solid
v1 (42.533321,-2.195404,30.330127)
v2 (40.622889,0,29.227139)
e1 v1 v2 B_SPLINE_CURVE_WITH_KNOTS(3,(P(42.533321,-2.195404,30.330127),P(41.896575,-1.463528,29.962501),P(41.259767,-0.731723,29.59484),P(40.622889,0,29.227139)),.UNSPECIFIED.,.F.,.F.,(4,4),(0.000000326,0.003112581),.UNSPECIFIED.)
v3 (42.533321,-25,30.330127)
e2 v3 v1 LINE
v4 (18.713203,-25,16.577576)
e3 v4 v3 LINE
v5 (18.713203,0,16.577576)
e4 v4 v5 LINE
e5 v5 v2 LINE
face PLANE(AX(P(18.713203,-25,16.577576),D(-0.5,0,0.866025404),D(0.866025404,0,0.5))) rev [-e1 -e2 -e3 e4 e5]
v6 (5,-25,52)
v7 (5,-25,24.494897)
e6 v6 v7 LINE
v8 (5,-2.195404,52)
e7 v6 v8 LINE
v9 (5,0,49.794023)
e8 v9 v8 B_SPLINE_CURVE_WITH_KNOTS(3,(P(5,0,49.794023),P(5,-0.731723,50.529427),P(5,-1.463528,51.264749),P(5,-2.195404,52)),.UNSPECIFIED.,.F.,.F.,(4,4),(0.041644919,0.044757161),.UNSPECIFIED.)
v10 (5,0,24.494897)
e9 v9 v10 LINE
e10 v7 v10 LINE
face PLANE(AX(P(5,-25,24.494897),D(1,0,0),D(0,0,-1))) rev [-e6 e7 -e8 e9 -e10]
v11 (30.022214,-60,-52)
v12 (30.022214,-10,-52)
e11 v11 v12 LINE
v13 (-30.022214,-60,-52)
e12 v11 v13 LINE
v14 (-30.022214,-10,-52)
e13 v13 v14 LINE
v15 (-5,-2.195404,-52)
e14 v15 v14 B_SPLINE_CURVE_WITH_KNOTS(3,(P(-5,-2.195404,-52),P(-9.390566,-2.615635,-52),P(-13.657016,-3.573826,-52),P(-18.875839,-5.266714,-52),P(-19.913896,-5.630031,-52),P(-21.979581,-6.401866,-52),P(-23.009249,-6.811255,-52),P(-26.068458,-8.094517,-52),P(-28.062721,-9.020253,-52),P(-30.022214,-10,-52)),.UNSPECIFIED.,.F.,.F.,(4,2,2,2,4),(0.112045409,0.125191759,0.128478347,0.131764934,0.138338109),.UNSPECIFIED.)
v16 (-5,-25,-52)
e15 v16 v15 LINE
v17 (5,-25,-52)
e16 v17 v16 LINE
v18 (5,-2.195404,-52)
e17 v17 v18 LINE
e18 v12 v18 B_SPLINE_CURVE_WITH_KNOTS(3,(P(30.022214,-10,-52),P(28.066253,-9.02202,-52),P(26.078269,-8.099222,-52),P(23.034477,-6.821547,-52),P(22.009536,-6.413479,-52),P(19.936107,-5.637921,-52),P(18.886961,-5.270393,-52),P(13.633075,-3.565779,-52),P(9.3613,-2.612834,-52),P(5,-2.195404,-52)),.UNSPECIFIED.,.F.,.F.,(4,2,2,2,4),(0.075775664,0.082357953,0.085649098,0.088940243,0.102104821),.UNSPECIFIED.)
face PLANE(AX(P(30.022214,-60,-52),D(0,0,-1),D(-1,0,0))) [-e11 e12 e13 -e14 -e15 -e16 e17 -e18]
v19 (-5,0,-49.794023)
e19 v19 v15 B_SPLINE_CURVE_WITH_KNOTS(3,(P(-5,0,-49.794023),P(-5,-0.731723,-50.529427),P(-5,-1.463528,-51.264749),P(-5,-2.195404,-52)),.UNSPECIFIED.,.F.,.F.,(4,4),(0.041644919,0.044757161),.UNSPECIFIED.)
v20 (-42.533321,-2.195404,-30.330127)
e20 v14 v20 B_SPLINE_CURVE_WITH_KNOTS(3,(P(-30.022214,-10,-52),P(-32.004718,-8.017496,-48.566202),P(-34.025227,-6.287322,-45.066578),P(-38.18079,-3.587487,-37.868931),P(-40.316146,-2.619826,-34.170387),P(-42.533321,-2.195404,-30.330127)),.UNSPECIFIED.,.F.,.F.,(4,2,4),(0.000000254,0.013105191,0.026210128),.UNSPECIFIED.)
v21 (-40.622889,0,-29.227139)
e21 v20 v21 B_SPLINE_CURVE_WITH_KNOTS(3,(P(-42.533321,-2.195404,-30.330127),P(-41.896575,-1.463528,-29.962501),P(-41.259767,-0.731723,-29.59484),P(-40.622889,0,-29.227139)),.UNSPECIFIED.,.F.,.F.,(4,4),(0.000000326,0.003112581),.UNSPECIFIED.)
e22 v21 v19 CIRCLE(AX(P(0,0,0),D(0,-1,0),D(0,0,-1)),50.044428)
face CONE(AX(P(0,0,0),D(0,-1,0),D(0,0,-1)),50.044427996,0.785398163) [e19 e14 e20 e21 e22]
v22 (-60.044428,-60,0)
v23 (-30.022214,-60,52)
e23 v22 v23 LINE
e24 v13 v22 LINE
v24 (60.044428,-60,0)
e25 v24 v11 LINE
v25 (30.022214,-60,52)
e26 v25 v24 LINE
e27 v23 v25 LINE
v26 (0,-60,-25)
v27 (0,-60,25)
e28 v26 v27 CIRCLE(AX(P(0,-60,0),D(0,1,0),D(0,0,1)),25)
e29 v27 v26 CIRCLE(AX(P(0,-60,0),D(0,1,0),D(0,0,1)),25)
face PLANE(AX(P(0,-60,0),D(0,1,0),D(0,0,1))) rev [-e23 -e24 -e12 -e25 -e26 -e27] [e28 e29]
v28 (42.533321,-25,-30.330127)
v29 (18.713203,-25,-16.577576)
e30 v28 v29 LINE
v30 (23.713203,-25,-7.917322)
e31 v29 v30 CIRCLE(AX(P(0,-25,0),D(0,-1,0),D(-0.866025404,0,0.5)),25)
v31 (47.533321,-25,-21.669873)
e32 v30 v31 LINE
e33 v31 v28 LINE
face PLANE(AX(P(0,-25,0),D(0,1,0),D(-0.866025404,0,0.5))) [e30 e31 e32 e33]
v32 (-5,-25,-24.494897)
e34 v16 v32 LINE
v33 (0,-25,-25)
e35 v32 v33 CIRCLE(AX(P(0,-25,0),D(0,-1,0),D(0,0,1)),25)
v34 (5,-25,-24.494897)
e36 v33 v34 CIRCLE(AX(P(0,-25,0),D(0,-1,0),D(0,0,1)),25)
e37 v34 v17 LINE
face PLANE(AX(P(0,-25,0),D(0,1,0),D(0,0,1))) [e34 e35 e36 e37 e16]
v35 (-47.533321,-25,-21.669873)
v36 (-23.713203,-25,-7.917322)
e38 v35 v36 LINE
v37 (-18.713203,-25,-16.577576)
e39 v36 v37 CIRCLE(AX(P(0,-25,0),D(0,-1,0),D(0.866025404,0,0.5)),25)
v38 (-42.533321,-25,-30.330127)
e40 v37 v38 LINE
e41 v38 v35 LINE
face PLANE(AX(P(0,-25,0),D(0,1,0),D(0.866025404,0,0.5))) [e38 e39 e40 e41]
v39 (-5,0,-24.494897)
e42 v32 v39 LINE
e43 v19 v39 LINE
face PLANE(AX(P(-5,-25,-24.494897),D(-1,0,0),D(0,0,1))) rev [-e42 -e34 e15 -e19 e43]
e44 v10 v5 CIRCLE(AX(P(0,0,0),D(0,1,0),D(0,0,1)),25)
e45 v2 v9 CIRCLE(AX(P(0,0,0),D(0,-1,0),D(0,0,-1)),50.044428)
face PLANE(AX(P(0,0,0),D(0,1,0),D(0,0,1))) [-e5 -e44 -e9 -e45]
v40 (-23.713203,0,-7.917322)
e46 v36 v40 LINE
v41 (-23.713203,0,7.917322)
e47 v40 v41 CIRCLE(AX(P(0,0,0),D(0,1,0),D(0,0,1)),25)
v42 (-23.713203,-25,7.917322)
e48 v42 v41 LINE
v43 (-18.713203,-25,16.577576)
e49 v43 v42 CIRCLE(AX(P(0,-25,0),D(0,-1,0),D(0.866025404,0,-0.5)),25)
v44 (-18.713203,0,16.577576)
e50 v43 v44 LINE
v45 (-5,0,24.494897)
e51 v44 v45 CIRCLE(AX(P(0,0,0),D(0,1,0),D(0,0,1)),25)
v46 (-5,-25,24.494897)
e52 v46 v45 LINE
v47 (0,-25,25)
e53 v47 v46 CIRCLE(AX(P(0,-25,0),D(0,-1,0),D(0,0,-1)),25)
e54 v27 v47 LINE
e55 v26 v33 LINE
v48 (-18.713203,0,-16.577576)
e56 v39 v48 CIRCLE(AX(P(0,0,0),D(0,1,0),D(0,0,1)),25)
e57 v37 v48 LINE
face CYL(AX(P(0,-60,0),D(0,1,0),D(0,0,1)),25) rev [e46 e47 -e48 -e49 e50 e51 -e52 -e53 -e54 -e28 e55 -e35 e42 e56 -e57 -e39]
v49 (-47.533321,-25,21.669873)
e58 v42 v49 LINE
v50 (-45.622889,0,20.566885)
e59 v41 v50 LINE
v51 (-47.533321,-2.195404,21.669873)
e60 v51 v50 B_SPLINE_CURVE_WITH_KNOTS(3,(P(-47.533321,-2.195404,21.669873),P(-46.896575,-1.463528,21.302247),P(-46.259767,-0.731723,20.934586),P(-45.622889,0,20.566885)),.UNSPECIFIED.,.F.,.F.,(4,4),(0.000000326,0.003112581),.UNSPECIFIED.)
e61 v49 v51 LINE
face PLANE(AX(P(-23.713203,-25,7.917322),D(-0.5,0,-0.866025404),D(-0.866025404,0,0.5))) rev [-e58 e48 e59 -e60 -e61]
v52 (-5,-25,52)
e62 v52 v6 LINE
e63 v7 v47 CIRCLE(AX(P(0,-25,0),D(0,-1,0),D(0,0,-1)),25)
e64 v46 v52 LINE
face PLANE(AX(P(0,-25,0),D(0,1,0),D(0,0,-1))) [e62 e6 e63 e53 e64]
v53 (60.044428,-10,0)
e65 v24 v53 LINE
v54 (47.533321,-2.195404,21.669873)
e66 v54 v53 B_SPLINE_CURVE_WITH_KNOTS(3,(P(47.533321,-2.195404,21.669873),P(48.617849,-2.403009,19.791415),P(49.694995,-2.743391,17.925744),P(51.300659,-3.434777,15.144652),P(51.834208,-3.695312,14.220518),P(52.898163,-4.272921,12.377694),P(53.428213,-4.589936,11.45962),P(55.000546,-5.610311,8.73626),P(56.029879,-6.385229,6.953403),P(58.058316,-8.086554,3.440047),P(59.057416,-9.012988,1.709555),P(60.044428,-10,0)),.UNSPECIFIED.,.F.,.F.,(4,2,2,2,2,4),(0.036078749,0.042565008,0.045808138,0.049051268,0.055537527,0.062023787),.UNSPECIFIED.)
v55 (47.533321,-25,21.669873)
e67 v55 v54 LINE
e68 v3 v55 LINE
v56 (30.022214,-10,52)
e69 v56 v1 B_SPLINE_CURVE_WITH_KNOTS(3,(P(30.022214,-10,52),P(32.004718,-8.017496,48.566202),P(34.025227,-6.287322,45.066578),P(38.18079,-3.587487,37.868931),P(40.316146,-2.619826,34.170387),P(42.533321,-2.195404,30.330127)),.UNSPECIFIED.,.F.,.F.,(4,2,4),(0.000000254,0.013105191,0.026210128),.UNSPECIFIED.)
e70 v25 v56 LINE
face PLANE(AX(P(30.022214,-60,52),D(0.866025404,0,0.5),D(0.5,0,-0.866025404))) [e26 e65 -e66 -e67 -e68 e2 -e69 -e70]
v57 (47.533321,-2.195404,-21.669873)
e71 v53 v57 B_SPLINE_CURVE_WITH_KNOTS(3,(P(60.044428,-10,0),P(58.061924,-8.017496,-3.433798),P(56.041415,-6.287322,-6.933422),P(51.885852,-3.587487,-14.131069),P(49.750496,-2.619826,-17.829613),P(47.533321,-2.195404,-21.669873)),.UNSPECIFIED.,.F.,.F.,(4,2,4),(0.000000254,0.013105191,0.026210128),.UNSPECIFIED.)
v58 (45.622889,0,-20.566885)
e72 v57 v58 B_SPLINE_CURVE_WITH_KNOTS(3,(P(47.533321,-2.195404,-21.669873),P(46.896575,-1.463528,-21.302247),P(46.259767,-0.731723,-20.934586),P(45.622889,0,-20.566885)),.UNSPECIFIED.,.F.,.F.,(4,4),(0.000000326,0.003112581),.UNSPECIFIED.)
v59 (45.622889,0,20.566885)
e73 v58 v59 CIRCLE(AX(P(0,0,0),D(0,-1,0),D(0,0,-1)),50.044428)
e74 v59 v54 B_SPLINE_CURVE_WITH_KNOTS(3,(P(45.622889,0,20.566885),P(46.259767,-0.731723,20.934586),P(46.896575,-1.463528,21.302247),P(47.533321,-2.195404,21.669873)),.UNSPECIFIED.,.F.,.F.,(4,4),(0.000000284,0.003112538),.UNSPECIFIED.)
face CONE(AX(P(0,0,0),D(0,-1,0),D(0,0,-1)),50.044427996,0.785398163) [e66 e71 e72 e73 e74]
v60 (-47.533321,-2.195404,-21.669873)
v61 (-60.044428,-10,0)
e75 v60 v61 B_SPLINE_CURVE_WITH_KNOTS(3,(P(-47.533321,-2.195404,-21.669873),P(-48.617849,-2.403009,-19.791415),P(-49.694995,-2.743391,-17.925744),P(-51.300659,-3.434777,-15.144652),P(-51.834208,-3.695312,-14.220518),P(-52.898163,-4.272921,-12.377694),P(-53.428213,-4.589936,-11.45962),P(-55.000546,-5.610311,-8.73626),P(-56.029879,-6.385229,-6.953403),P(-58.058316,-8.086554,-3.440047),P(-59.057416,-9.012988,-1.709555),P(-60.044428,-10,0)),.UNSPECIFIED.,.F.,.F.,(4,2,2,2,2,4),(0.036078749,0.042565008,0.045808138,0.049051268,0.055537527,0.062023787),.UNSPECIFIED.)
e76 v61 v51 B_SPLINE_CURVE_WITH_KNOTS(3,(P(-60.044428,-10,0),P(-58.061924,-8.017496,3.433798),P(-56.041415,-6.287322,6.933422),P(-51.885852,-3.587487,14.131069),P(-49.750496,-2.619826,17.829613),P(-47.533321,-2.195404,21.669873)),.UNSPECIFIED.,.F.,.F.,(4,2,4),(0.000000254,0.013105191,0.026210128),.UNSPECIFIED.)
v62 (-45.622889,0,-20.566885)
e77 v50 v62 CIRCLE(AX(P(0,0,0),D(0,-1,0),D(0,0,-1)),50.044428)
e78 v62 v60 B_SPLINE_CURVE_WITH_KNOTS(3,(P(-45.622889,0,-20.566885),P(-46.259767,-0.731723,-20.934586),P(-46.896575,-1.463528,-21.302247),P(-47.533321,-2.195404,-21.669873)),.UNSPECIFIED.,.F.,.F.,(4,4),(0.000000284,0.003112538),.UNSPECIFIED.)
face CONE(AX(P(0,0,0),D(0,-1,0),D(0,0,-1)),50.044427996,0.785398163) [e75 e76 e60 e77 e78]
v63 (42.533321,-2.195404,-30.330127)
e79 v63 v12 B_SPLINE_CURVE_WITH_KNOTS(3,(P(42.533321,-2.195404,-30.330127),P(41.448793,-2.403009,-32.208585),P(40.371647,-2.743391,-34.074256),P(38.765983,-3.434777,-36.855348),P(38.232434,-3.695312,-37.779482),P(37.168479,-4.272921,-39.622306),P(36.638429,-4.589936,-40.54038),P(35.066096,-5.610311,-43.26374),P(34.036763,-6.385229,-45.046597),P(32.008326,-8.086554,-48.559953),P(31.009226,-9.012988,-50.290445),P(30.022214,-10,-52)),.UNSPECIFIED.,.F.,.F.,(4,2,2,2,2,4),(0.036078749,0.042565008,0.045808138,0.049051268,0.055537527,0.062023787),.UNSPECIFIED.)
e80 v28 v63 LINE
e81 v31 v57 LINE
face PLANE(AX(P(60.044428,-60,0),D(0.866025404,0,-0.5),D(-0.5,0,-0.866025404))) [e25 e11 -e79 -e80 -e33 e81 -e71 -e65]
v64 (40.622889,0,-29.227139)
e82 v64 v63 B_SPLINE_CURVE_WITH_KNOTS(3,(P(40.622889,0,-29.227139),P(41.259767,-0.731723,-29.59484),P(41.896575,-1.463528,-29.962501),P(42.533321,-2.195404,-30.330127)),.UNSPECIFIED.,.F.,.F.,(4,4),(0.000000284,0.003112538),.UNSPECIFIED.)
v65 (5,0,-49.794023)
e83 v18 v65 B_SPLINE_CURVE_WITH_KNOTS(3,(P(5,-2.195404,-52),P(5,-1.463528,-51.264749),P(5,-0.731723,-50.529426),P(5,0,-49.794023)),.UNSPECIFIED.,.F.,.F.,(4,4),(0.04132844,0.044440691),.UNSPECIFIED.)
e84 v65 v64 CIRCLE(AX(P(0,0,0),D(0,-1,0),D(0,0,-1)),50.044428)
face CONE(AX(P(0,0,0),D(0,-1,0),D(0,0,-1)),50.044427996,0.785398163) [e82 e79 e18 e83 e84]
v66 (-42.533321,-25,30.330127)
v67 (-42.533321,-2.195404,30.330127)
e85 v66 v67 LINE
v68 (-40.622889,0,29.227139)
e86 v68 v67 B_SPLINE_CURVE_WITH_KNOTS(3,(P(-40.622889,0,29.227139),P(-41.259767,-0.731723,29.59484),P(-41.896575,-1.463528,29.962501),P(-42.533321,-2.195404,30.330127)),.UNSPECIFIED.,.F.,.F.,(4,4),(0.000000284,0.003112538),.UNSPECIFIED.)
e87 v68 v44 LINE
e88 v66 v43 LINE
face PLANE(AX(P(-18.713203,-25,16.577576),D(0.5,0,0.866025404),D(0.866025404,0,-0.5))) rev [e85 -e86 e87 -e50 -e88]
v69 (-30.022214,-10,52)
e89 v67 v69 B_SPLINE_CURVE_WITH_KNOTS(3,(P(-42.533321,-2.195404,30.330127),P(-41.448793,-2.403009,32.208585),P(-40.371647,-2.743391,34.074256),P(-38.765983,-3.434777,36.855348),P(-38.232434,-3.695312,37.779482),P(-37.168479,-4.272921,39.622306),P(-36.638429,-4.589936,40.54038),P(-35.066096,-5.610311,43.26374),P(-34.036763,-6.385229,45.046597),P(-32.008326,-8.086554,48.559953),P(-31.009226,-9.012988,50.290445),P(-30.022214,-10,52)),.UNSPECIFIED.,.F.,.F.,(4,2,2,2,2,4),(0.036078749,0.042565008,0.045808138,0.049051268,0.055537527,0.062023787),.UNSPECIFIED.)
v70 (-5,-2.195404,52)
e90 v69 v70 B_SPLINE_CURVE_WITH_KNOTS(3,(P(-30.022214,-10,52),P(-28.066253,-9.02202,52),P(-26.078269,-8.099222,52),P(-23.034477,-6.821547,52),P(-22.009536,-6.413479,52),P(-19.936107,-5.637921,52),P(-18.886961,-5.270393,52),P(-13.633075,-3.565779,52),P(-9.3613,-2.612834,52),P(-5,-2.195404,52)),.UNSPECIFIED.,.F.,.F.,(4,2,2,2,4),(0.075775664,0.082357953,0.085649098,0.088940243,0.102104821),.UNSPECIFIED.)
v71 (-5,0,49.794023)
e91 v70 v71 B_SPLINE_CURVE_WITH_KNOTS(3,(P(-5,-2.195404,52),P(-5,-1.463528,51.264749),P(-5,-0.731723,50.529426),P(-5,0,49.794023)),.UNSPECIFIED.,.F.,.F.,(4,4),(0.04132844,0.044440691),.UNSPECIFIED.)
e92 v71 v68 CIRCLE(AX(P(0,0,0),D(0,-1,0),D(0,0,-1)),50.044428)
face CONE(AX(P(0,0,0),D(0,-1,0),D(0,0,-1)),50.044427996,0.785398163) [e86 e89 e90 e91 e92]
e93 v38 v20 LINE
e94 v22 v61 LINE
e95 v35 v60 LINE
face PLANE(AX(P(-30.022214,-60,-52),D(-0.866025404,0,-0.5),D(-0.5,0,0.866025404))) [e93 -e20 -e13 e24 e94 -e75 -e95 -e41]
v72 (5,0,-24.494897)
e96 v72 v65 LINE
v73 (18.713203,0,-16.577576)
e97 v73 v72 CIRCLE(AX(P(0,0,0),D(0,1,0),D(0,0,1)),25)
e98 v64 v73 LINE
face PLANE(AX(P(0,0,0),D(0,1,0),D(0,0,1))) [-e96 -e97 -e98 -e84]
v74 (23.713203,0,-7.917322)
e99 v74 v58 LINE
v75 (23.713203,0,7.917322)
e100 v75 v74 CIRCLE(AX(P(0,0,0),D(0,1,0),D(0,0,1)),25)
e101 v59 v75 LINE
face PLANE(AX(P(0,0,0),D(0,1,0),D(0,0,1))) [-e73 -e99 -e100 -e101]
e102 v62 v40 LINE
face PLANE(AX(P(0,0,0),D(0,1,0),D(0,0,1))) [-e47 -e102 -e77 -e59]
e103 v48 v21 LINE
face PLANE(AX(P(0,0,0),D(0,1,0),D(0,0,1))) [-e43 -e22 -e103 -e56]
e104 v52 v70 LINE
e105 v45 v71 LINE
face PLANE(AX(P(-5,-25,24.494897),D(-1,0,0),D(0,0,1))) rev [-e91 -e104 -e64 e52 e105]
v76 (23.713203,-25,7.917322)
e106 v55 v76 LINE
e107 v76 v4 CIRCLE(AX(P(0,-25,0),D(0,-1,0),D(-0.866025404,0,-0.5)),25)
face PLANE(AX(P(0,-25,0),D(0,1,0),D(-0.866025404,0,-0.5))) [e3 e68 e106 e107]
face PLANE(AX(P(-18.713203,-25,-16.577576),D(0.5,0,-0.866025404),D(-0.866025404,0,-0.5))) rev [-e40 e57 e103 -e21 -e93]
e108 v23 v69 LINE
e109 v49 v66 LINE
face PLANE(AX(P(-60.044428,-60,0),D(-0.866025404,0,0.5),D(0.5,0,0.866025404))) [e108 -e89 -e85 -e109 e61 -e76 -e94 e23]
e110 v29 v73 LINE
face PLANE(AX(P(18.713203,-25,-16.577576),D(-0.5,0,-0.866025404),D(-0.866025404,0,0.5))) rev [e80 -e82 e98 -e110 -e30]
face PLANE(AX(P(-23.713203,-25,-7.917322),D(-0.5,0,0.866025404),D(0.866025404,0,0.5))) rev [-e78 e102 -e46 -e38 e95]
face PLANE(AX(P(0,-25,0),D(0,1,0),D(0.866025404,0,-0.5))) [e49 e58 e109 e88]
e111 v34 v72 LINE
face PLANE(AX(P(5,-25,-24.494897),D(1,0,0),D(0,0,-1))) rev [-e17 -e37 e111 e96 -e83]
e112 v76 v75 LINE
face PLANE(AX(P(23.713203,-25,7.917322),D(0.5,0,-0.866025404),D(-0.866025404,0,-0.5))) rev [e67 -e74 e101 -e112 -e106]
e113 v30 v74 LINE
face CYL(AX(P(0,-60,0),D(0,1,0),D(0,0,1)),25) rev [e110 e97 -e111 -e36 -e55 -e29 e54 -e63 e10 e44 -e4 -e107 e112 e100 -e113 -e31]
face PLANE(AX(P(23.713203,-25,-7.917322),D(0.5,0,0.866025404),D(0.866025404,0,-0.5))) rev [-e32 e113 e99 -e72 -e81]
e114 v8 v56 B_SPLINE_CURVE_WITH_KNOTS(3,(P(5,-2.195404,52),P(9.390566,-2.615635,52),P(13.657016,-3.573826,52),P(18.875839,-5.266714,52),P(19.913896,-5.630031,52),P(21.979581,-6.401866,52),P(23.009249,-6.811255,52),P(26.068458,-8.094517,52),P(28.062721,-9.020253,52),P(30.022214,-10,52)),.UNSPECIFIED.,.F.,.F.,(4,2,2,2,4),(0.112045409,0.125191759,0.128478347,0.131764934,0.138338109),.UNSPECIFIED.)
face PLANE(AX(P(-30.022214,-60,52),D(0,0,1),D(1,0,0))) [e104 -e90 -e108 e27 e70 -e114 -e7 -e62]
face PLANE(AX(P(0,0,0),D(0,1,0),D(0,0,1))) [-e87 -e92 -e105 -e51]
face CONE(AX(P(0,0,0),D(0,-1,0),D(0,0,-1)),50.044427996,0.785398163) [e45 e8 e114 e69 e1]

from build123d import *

# Parameters (mm, degrees)
HEX_PROFILE_R                      = 25
HEX_NUT_BODY_DEPTH                 = 60
CASTELLATION_SLOT_10_WIDE_DEPTH    = 25
CASTELLATION_SLOT_PATTERN_6X_COUNT = 6


with BuildPart() as part:
    # Hex Profile → Hex Nut Body (new body)
    with BuildSketch(Plane(origin=(0, 0, 0), x_dir=(1, 0, 0), z_dir=(0, 1, 0))):
        Polygon((60.044427996, 0), (30.022213998, 52), (-30.022213998, 52), (-60.044427996, 0), (-30.022213998, -52), (30.022213998, -52), align=None)
        with Locations(Location((0, 0, 0), (0, 0, 270))):
            Circle(HEX_PROFILE_R, mode=Mode.SUBTRACT)
    extrude(amount=-HEX_NUT_BODY_DEPTH)

    # Top Chamfer Profile → Top Chamfer 10x10 (revolve, cut)
    with BuildSketch(Plane.XY, mode=Mode.PRIVATE) as top_chamfer_10x10_sk:
        Polygon((50.044427996, 0), (60.044427996, -10), (60.044427996, 0), align=None)
    revolve(top_chamfer_10x10_sk.sketch.rotate(Axis((0, -60, 0), (0, 1, 0)), 90), axis=Axis((0, -60, 0), (0, 1, 0)), mode=Mode.SUBTRACT)

    # Castellation Slot Profile → Castellation Slot 10 Wide (cut)
    with BuildSketch(Plane(origin=(0, 0, 0), x_dir=(1, 0, 0), z_dir=(0, 1, 0))):
        with BuildLine():
            Line((-5, 24.494897428), (-5, 52))
            Line((-5, 52), (5, 52))
            Line((5, 52), (5, 24.494897428))
            ThreePointArc((5, 24.494897428), (0, 25), (-5, 24.494897428))
        make_face()
    castellation_slot_10_wide = extrude(amount=-CASTELLATION_SLOT_10_WIDE_DEPTH, mode=Mode.SUBTRACT)

    # Castellation Slot Pattern 6x: Castellation Slot 10 Wide ×6 about axis
    castellation_slot_pattern_6x_axis = Axis((0, 0, 0), (0, 1, 0))
    for i in range(1, CASTELLATION_SLOT_PATTERN_6X_COUNT):
        add(castellation_slot_10_wide.rotate(castellation_slot_pattern_6x_axis, i * 360 / CASTELLATION_SLOT_PATTERN_6X_COUNT), mode=Mode.SUBTRACT)


solid = part.part
